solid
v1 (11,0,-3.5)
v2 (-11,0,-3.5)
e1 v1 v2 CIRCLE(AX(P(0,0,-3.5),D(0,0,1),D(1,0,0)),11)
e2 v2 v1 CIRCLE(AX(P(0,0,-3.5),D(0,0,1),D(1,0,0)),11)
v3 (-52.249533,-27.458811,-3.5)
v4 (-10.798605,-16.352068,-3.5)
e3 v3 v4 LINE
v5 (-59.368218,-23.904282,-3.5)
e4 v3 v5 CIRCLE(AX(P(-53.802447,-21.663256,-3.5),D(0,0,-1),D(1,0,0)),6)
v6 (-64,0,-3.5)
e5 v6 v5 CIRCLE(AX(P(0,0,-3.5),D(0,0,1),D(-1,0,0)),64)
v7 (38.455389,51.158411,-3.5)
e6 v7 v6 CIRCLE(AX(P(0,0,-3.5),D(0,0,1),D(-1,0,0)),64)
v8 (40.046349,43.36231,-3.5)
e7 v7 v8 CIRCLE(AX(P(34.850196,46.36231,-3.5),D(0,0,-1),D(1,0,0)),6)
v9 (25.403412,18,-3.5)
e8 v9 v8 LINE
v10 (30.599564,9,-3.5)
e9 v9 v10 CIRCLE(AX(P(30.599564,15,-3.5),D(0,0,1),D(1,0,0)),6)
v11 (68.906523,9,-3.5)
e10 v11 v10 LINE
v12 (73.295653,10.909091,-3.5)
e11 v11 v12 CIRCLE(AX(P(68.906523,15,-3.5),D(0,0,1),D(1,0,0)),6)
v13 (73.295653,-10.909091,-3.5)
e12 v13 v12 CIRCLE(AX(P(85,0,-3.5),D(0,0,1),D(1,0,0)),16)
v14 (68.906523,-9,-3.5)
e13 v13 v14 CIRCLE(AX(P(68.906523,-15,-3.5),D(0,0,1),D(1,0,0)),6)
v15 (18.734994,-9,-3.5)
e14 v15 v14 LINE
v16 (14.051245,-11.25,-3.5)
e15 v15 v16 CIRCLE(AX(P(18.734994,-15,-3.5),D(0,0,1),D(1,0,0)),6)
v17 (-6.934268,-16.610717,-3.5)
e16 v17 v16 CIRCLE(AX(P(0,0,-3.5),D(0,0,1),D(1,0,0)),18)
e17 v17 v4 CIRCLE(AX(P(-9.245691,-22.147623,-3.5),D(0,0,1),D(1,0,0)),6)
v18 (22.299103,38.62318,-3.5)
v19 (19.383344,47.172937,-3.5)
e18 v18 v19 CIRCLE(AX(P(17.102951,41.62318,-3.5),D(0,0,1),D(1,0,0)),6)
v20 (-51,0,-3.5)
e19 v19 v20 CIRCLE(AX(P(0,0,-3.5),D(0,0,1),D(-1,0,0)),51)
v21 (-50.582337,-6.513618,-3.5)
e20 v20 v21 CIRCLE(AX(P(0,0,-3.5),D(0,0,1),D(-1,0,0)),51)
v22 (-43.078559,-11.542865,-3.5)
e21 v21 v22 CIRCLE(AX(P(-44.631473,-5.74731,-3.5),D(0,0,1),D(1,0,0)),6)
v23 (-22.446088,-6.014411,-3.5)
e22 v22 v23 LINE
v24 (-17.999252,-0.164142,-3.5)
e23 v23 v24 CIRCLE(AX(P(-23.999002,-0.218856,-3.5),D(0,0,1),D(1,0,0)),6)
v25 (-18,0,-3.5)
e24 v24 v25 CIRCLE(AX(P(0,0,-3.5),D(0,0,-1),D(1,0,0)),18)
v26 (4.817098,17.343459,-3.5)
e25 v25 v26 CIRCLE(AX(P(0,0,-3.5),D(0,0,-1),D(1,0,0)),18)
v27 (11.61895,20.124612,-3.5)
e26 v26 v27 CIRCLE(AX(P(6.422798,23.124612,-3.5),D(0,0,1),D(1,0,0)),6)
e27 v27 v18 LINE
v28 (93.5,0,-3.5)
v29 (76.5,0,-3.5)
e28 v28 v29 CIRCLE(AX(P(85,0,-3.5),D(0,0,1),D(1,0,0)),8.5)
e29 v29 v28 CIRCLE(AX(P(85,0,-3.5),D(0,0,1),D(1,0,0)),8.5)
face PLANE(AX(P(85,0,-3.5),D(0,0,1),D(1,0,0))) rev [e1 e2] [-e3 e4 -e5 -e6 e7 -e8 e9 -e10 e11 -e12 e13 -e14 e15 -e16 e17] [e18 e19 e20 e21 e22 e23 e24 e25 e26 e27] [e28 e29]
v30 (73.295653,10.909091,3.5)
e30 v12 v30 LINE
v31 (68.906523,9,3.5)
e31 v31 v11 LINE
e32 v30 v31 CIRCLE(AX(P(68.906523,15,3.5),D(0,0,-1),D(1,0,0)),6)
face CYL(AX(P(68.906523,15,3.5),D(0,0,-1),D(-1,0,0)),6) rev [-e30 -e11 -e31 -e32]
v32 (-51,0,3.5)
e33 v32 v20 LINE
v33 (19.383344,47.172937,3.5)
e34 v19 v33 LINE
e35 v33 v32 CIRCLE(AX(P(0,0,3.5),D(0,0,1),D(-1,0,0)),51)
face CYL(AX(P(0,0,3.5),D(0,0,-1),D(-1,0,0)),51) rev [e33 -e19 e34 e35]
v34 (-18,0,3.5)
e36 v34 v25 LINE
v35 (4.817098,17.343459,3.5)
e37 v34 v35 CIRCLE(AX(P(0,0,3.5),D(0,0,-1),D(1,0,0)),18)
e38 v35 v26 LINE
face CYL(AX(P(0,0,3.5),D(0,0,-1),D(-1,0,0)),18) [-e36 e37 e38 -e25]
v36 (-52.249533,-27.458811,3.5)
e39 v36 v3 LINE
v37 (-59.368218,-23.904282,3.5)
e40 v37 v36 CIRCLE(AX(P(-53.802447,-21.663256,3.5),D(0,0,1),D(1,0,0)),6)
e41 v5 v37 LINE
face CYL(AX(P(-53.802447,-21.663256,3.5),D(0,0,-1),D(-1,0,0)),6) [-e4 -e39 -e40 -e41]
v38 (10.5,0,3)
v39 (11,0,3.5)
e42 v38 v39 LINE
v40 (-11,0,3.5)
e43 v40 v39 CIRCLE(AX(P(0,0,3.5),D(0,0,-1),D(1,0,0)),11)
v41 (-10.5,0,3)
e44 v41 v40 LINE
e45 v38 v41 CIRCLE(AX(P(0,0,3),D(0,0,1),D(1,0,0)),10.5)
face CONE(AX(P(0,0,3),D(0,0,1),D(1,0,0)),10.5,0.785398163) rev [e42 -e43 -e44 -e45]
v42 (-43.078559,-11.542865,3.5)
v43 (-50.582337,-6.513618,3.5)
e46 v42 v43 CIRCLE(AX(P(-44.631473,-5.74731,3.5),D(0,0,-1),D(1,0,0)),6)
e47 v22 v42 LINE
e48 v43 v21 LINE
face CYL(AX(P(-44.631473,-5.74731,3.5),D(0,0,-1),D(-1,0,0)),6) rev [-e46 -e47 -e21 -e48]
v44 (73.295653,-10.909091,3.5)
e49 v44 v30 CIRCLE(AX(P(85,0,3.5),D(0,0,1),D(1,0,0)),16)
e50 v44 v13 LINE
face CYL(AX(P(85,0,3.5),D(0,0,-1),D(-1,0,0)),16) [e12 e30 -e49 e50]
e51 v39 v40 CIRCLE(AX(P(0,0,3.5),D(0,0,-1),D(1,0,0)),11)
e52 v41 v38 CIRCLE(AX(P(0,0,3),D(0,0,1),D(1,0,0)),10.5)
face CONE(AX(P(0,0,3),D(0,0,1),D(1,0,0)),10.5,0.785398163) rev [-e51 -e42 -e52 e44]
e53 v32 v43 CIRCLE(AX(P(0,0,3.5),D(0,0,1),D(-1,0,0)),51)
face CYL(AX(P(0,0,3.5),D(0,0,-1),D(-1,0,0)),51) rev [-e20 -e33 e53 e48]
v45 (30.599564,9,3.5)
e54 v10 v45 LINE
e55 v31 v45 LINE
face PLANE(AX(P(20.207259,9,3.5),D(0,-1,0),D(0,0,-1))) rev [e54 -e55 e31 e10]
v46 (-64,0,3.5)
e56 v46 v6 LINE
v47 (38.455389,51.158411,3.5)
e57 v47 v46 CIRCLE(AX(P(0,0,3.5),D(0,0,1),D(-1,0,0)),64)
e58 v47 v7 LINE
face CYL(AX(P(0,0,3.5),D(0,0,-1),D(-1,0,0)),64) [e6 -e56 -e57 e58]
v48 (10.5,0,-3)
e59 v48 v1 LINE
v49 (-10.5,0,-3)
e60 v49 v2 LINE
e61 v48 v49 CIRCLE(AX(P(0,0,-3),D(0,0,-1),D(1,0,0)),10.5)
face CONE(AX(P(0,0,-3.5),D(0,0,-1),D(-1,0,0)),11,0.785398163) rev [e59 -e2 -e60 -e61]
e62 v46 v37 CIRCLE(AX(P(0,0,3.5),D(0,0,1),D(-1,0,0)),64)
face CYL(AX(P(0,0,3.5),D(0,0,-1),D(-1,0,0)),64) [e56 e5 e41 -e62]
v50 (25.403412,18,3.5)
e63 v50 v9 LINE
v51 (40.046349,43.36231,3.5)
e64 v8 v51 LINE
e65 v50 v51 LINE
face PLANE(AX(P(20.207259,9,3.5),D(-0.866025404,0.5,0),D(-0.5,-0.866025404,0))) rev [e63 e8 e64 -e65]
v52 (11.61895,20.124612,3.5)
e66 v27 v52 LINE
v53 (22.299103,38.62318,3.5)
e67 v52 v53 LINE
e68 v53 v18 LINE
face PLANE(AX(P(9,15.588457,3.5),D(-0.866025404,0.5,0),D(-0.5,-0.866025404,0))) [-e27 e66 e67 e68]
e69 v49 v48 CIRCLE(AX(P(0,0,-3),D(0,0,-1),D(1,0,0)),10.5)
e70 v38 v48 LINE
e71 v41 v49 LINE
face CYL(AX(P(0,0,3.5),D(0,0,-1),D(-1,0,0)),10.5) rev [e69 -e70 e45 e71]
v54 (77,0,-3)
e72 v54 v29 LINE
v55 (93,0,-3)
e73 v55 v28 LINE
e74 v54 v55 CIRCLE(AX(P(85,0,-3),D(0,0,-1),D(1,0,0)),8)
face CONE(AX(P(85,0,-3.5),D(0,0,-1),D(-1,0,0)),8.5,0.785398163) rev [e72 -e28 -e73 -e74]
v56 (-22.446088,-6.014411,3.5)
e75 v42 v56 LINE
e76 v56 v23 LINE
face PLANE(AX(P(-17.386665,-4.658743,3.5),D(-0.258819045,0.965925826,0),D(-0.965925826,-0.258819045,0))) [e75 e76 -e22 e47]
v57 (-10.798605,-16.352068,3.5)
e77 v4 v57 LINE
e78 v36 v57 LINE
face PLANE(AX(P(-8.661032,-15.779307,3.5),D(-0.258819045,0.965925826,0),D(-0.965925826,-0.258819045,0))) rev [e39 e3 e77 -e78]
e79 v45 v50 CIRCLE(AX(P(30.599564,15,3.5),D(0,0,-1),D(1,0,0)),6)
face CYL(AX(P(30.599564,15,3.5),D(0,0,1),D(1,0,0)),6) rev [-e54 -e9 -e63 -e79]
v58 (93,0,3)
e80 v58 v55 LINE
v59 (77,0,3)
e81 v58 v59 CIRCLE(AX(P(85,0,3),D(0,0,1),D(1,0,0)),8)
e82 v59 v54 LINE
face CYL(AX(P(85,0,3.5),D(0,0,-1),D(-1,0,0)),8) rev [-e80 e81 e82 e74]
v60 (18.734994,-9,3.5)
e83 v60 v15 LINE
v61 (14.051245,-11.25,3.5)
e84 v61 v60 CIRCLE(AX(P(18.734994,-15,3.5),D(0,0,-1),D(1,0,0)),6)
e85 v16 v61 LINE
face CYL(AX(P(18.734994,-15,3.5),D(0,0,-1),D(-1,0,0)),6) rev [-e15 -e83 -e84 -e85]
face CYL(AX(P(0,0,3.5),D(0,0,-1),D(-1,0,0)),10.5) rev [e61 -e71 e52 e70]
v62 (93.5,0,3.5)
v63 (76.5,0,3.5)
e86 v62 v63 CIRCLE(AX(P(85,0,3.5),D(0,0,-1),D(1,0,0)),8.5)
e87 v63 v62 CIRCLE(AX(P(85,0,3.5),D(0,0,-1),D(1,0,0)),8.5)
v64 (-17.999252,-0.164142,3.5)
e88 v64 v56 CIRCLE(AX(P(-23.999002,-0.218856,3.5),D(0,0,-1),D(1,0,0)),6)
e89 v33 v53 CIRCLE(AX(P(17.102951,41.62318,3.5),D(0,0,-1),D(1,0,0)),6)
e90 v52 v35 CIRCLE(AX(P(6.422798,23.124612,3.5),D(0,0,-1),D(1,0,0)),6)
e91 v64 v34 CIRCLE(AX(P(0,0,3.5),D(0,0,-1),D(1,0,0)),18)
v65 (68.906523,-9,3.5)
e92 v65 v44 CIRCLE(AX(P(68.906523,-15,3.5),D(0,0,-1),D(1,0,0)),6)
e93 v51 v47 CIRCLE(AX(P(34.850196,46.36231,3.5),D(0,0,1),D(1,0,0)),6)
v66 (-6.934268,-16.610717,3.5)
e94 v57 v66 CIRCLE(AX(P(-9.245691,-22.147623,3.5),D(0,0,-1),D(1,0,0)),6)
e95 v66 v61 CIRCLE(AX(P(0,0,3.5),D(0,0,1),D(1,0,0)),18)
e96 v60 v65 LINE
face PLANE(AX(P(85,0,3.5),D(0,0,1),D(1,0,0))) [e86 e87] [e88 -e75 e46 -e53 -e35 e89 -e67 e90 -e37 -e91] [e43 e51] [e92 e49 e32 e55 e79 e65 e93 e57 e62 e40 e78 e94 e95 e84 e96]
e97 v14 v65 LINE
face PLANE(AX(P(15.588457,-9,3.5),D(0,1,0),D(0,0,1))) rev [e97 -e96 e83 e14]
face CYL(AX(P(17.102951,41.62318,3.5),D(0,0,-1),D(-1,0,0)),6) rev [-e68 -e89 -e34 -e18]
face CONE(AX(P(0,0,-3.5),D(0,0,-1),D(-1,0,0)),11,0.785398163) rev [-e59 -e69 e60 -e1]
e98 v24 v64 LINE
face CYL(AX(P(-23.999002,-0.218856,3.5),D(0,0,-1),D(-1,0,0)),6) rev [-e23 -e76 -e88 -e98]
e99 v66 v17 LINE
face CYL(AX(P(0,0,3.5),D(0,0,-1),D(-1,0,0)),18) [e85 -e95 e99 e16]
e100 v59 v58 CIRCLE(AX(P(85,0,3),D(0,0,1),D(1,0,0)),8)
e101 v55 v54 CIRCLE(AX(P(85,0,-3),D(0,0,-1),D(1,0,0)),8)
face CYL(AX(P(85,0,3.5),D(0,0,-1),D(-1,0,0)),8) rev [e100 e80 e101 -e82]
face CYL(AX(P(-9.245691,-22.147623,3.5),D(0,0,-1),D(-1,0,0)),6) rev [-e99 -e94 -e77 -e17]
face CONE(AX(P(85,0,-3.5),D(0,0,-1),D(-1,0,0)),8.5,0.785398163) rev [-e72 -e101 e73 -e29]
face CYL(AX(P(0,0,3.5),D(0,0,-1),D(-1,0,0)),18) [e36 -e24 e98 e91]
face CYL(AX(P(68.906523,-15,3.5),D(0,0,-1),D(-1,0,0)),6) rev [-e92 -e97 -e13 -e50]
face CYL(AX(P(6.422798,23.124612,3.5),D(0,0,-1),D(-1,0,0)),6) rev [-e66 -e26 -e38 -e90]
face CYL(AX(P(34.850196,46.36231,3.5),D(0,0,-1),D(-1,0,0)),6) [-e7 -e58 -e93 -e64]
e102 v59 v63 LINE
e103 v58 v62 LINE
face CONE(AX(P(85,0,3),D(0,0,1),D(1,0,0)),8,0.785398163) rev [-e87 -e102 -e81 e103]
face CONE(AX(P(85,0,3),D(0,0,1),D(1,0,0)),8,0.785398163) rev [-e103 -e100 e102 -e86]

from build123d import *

# Parameters (mm, degrees)
OPENER_PROFILE_SKETCH_R   = 8
OPENER_PROFILE_SKETCH_R_2 = 10.5
OPENER_PLATE_7MM_DEPTH    = 3.5
EDGE_FILLETS_R6_R         = 6
EDGE_CHAMFERS_0_5X45_SIZE = 0.5


with BuildPart() as part:
    # Opener Profile Sketch → Opener Plate 7mm (new, symmetric)
    with BuildSketch(Plane.XY):
        with BuildLine():
            Line((20.207259422, 9), (71.771243445, 9))
            ThreePointArc((71.771243445, 9), (101, 0), (71.771243445, -9))
            Line((71.771243445, -9), (15.588457268, -9))
            ThreePointArc((15.588457268, -9), (4.846344572, -17.335309178), (-8.66103197, -15.779306867))
            Line((-8.66103197, -15.779306867), (-57.165847871, -28.776133117))
            ThreePointArc((-57.165847871, -28.776133117), (-38.960731457, 50.774613779), (42.591220317, 47.770157545))
            Line((42.591220317, 47.770157545), (20.207259422, 9))
        make_face()
        with Locations((85, 0)):
            Circle(OPENER_PROFILE_SKETCH_R, mode=Mode.SUBTRACT)
        Circle(OPENER_PROFILE_SKETCH_R_2, mode=Mode.SUBTRACT)
        with BuildLine():
            Line((9, 15.588457268), (25.5, 44.167295593))
            ThreePointArc((25.5, 44.167295593), (-31.046832879, 40.461020355), (-49.262217141, -13.1997713))
            Line((-49.262217141, -13.1997713), (-17.386664873, -4.658742812))
            ThreePointArc((-17.386664873, -4.658742812), (-10.957705722, 14.280360125), (9, 15.588457268))
        make_face(mode=Mode.SUBTRACT)
    extrude(amount=OPENER_PLATE_7MM_DEPTH, both=True)

    # Edge Fillets R6
    edge_fillets_r6_edges = [part.edges().sort_by_distance(p)[0] for p in [
        (71.771243445, -9, 0),
        (15.588457268, -9, 0),
        (-8.66103197, -15.779306867, 0),
        (-57.165847871, -28.776133117, 0),
        (42.591220317, 47.770157545, 0),
        (20.207259422, 9, 0),
        (71.771243445, 9, 0),
        (-17.386664873, -4.658742812, 0),
        (9, 15.588457268, 0),
        (25.5, 44.167295593, 0),
        (-49.262217141, -13.1997713, 0),
    ]]
    fillet(edge_fillets_r6_edges, radius=EDGE_FILLETS_R6_R)

    # Edge Chamfers 0.5x45
    edge_chamfers_0_5x45_edges = [part.edges().sort_by_distance(p)[0] for p in [
        (77, 0, -3.5),
        (77, 0, 3.5),
        (-10.5, 0, -3.5),
        (-10.5, 0, 3.5),
    ]]
    chamfer(edge_chamfers_0_5x45_edges, length=EDGE_CHAMFERS_0_5X45_SIZE)


solid = part.part
